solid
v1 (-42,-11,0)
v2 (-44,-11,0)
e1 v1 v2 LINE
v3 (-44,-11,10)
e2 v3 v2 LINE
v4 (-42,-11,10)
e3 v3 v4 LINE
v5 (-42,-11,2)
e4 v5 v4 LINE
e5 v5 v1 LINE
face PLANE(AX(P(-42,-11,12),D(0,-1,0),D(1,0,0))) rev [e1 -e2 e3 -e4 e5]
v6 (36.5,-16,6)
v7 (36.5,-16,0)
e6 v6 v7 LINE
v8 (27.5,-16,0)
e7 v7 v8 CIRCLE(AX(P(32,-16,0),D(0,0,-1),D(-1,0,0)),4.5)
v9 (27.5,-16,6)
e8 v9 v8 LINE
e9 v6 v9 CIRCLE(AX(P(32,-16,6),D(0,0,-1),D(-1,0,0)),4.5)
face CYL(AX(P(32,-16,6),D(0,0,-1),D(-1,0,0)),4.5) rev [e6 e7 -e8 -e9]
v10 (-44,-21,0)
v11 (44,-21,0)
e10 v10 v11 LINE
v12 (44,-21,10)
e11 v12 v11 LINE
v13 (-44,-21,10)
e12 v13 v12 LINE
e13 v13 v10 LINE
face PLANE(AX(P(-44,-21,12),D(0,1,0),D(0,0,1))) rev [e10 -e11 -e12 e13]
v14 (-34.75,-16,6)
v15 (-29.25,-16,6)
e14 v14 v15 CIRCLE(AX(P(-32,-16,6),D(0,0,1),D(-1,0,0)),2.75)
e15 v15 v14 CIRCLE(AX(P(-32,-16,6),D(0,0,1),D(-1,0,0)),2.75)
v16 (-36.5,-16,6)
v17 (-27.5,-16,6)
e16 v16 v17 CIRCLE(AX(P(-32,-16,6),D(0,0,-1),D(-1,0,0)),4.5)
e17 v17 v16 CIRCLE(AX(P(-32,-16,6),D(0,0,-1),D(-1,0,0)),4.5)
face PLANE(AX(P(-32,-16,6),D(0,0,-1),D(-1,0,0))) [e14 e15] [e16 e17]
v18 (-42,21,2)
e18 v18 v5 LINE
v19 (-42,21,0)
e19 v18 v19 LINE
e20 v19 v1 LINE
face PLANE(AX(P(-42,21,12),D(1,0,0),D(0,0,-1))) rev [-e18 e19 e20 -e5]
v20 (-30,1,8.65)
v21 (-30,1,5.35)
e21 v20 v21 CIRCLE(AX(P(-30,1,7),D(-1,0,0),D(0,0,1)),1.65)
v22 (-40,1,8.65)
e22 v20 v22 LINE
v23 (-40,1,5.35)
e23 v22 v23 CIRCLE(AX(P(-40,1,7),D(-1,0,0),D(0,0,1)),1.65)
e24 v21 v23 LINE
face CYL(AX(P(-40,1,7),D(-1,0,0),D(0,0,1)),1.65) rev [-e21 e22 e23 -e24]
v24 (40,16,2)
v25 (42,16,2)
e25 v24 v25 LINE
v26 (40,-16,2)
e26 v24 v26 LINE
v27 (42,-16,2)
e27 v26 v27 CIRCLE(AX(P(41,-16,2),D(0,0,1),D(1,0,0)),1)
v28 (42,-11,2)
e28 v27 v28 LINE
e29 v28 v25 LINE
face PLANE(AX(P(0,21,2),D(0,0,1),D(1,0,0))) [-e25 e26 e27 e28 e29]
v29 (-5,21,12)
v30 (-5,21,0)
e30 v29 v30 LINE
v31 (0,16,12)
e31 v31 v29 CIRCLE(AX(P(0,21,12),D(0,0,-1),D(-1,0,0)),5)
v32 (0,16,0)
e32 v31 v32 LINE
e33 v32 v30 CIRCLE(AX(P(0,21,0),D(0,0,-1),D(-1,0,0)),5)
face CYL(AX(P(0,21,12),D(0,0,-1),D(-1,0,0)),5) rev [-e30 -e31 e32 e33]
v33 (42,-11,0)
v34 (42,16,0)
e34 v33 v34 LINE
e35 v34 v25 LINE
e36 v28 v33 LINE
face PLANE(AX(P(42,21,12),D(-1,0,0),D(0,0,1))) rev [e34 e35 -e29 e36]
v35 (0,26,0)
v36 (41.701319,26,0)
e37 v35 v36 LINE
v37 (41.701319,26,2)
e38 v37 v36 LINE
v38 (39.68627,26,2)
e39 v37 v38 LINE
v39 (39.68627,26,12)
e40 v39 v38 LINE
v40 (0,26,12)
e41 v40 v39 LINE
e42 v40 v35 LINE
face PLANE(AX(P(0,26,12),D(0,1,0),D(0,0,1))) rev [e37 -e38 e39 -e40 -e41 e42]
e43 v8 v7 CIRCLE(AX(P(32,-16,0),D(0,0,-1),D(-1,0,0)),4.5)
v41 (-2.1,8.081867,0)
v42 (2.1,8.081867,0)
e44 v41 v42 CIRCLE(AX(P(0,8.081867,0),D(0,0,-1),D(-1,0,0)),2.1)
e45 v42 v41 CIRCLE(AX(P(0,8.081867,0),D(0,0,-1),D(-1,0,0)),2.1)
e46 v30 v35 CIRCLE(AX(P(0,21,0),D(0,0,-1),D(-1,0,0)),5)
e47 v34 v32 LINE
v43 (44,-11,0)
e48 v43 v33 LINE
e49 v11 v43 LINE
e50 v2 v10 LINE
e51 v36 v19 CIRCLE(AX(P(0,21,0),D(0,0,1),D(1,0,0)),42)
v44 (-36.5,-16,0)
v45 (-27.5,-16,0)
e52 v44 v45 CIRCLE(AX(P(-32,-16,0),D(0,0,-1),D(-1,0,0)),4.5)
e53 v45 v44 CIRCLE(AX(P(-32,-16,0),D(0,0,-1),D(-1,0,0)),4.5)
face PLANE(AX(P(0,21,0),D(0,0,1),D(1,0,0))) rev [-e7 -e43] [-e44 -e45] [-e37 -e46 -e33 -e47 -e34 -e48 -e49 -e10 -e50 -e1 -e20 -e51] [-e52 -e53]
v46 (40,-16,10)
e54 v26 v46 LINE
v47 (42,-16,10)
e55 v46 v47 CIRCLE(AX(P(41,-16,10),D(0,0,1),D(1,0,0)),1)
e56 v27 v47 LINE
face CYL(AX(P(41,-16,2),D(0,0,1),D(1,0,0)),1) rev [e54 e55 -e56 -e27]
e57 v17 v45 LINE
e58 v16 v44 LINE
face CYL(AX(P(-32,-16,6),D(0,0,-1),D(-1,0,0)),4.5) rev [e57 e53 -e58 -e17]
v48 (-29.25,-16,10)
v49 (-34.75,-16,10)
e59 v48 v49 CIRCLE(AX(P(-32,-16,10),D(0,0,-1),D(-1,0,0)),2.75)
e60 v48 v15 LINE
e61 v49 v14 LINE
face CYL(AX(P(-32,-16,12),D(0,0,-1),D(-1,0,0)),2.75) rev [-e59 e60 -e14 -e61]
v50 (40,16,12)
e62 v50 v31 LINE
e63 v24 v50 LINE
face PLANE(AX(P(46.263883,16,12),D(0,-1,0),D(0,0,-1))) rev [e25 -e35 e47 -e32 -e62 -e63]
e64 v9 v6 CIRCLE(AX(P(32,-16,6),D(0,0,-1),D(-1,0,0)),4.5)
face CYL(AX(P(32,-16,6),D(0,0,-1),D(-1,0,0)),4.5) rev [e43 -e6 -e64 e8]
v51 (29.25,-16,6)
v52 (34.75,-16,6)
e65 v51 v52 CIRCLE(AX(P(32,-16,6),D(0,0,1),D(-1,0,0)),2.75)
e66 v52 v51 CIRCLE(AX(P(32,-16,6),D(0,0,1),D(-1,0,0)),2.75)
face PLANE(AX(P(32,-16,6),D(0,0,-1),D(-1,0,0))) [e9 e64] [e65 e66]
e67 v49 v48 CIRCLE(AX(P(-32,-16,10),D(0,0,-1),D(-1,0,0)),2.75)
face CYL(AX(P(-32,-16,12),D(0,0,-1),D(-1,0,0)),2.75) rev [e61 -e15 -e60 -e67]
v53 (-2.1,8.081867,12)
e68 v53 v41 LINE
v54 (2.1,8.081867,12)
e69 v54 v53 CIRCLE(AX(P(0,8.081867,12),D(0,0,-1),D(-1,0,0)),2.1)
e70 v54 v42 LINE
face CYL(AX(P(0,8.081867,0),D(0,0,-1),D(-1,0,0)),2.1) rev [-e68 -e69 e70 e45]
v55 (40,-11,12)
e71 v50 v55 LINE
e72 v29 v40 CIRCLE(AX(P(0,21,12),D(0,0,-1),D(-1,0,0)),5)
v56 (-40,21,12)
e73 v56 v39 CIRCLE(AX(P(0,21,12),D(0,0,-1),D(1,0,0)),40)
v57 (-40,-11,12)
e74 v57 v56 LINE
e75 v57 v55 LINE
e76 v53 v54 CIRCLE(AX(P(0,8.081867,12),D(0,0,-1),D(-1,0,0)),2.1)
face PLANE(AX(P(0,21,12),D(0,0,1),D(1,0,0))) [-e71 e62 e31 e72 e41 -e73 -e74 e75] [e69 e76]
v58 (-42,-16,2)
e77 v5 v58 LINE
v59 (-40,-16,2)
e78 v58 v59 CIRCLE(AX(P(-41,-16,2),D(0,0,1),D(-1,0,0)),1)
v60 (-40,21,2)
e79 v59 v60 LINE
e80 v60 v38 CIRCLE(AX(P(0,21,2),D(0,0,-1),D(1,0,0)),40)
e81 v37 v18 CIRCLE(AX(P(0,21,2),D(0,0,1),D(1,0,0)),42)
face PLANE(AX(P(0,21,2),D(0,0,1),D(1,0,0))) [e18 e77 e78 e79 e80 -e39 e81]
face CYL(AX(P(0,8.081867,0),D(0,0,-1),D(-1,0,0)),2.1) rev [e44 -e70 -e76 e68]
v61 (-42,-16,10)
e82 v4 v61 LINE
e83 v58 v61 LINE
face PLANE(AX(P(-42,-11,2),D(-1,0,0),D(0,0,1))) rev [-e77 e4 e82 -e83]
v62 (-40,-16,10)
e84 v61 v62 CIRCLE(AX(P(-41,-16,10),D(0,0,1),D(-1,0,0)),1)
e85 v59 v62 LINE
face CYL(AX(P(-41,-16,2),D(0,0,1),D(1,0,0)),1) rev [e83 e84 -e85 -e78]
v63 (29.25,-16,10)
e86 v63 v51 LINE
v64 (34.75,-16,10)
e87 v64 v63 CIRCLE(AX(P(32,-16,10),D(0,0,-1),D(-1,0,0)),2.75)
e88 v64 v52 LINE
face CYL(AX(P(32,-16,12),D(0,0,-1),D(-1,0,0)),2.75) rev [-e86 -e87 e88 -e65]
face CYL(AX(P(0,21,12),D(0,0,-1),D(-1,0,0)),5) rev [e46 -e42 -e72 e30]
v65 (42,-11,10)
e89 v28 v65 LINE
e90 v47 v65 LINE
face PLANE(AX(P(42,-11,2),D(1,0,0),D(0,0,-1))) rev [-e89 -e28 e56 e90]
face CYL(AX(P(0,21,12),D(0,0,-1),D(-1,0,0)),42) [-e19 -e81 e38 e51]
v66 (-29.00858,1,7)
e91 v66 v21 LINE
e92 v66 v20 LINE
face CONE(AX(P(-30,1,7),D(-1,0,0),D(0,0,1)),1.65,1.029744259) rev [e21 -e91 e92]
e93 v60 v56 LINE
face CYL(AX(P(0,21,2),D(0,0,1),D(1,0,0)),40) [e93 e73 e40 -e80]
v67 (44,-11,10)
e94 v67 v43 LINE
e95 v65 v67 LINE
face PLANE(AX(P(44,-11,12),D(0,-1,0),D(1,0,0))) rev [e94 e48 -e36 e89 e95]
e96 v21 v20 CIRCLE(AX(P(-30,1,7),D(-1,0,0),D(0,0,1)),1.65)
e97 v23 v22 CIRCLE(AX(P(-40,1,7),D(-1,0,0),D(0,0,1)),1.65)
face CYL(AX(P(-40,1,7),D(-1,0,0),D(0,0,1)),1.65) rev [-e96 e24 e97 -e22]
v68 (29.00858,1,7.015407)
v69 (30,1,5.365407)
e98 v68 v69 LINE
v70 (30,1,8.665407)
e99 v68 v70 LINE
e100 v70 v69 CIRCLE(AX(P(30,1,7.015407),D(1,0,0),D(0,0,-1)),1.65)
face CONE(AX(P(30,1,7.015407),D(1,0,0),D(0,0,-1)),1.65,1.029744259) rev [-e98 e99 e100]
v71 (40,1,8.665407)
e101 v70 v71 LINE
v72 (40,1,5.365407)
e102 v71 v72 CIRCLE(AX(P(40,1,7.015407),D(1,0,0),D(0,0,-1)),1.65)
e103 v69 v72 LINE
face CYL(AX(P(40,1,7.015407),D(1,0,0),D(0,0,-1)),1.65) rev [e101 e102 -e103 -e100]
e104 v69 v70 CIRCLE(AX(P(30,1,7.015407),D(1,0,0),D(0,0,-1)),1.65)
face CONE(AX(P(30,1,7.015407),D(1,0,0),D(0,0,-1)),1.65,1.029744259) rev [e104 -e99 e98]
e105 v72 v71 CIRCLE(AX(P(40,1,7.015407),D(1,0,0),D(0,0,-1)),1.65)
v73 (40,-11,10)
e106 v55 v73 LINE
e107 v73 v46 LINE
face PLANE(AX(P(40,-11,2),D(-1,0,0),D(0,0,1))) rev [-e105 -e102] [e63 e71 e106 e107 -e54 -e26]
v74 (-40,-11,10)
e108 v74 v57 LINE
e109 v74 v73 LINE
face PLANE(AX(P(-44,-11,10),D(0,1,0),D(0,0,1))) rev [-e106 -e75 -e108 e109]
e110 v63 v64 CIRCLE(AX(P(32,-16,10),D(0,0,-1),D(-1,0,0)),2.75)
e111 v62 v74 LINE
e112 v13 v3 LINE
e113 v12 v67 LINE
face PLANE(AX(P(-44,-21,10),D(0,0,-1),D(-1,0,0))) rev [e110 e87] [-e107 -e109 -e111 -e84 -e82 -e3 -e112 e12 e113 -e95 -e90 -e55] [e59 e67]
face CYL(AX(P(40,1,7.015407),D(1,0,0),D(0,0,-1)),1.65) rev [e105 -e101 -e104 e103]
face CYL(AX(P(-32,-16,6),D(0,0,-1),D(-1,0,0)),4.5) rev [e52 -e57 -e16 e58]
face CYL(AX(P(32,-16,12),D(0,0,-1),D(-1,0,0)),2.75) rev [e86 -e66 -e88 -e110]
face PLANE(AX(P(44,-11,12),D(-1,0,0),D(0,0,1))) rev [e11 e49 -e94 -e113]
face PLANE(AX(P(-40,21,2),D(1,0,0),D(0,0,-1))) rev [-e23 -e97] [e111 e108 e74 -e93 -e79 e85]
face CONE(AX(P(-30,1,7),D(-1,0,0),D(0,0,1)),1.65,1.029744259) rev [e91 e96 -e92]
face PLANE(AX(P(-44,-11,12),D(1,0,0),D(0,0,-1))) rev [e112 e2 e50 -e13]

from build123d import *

# Parameters (mm, degrees)
EXTRUDE_1_DEPTH        = 12
CUT_EXTRUDE_START      = -10
CUT_EXTRUDE_1_DEPTH    = 10
SKETCH_3_W             = 2
SKETCH_3_H             = 10
CUT_EXTRUDE_2_DEPTH    = 109.889852603
CUT_EXTRUDE_3_DEPTH    = 8
CUT_EXTRUDE_4_DEPTH    = 78.775317421
SKETCH_6_R             = 2.75
CUT_EXTRUDE_5_DEPTH    = 78.775317421
SKETCH_7_R             = 4.5
CUT_EXTRUDE_6_DEPTH    = 6
HOLE_WIZARD_M4_1_D     = 3.3
HOLE_WIZARD_M4_1_DEPTH = 10
HOLE_WIZARD_M4_1_TIP   = 0.991420021
HOLE_WIZARD_M4_2_D     = 3.3
HOLE_WIZARD_M4_2_DEPTH = 10
HOLE_WIZARD_M4_2_TIP   = 0.991420021
HOLE_WIZARD_M5_1_D     = 4.2


with BuildPart() as part:
    # 草图1 → 凸台-拉伸1 (new body)
    with BuildSketch(Plane.XY):
        with BuildLine():
            Line((-44, -11), (-44, -21))
            Line((-44, -21), (44, -21))
            Line((44, -21), (44, -11))
            Line((44, -11), (42, -11))
            Line((42, -11), (42, 21))
            ThreePointArc((42, 21), (0, 63), (-42, 21))
            Line((-42, 21), (-42, -11))
            Line((-42, -11), (-44, -11))
        make_face()
    extrude(amount=EXTRUDE_1_DEPTH)

    # 草图2 → 切除-拉伸1 (cut)
    with BuildSketch(Plane.XY.offset(12).offset(CUT_EXTRUDE_START)):
        with BuildLine():
            Line((-40, 21), (-40, -11))
            Line((-40, -11), (-42, -11))
            Line((-42, -11), (-42, 21))
            ThreePointArc((-42, 21), (0, 63), (42, 21))
            Line((42, 21), (42, -11))
            Line((42, -11), (40, -11))
            Line((40, -11), (40, 21))
            ThreePointArc((40, 21), (0, 61), (-40, 21))
        make_face()
    extrude(amount=CUT_EXTRUDE_1_DEPTH, mode=Mode.SUBTRACT)

    # 草图3 → 切除-拉伸2 (cut, through all)
    with BuildSketch(Plane(origin=(44, 0, 0), x_dir=(0, 0, -1), z_dir=(1, 0, 0))):
        with Locations((-11, -16)):
            Rectangle(SKETCH_3_W, SKETCH_3_H)
    extrude(amount=-CUT_EXTRUDE_2_DEPTH, mode=Mode.SUBTRACT)

    # 草图4 → 切除-拉伸3 (cut)
    with BuildSketch(Plane.XY.offset(10)):
        with BuildLine():
            Line((-40, -11), (-42, -11))
            Line((-42, -11), (-42, -16))
            ThreePointArc((-42, -16), (-41, -17), (-40, -16))
            Line((-40, -16), (-40, -11))
        make_face()
        with BuildLine():
            Line((42, -11), (42, -16))
            ThreePointArc((42, -16), (41, -17), (40, -16))
            Line((40, -16), (40, -11))
            Line((40, -11), (42, -11))
        make_face()
    extrude(amount=-CUT_EXTRUDE_3_DEPTH, mode=Mode.SUBTRACT)

    # 草图5 → 切除-拉伸4 (cut, through all)
    with BuildSketch(Plane(origin=(0, 0, 0), x_dir=(-1, 0, 0), z_dir=(0, 0, -1))):
        with BuildLine():
            Line((0, 26), (-46.263882953, 26))
            Line((-46.263882953, 26), (-46.263882953, 16))
            Line((-46.263882953, 16), (0, 16))
            ThreePointArc((0, 16), (5, 21), (0, 26))
        make_face()
    extrude(amount=-CUT_EXTRUDE_4_DEPTH, mode=Mode.SUBTRACT)

    # 草图6 → 切除-拉伸5 (cut, through all)
    with BuildSketch(Plane(origin=(0, 0, 0), x_dir=(-1, 0, 0), z_dir=(0, 0, -1))):
        with Locations((-32, -16)):
            Circle(SKETCH_6_R)
        with Locations((32, -16)):
            Circle(SKETCH_6_R)
    extrude(amount=-CUT_EXTRUDE_5_DEPTH, mode=Mode.SUBTRACT)

    # 草图7 → 切除-拉伸6 (cut)
    with BuildSketch(Plane(origin=(0, 0, 0), x_dir=(-1, 0, 0), z_dir=(0, 0, -1))):
        with Locations((-32, -16)):
            Circle(SKETCH_7_R)
        with Locations((32, -16)):
            Circle(SKETCH_7_R)
    extrude(amount=-CUT_EXTRUDE_6_DEPTH, mode=Mode.SUBTRACT)

    # M4 螺纹孔1
    with Locations(Plane(origin=(-40, 1, 7), x_dir=(0, 0, -1), z_dir=(-1, 0, 0))):
        with Locations((0, 0)):
            Hole(HOLE_WIZARD_M4_1_D / 2, depth=HOLE_WIZARD_M4_1_DEPTH)
            with Locations((0, 0, -(HOLE_WIZARD_M4_1_DEPTH + HOLE_WIZARD_M4_1_TIP / 2))):  # 118° drill point
                Cone(0, HOLE_WIZARD_M4_1_D / 2, HOLE_WIZARD_M4_1_TIP, mode=Mode.SUBTRACT)

    # M4 螺纹孔2
    with Locations(Plane(origin=(40, 1, 7.015407491), x_dir=(0, 0, 1), z_dir=(1, 0, 0))):
        with Locations((0, 0)):
            Hole(HOLE_WIZARD_M4_2_D / 2, depth=HOLE_WIZARD_M4_2_DEPTH)
            with Locations((0, 0, -(HOLE_WIZARD_M4_2_DEPTH + HOLE_WIZARD_M4_2_TIP / 2))):  # 118° drill point
                Cone(0, HOLE_WIZARD_M4_2_D / 2, HOLE_WIZARD_M4_2_TIP, mode=Mode.SUBTRACT)

    # M5 螺纹孔1 (through all)
    with Locations(Plane(origin=(0, 8.081866722, 0), x_dir=(-1, 0, 0), z_dir=(0, 0, -1))):
        with Locations((0, 0)):
            Hole(HOLE_WIZARD_M5_1_D / 2)


solid = part.part
